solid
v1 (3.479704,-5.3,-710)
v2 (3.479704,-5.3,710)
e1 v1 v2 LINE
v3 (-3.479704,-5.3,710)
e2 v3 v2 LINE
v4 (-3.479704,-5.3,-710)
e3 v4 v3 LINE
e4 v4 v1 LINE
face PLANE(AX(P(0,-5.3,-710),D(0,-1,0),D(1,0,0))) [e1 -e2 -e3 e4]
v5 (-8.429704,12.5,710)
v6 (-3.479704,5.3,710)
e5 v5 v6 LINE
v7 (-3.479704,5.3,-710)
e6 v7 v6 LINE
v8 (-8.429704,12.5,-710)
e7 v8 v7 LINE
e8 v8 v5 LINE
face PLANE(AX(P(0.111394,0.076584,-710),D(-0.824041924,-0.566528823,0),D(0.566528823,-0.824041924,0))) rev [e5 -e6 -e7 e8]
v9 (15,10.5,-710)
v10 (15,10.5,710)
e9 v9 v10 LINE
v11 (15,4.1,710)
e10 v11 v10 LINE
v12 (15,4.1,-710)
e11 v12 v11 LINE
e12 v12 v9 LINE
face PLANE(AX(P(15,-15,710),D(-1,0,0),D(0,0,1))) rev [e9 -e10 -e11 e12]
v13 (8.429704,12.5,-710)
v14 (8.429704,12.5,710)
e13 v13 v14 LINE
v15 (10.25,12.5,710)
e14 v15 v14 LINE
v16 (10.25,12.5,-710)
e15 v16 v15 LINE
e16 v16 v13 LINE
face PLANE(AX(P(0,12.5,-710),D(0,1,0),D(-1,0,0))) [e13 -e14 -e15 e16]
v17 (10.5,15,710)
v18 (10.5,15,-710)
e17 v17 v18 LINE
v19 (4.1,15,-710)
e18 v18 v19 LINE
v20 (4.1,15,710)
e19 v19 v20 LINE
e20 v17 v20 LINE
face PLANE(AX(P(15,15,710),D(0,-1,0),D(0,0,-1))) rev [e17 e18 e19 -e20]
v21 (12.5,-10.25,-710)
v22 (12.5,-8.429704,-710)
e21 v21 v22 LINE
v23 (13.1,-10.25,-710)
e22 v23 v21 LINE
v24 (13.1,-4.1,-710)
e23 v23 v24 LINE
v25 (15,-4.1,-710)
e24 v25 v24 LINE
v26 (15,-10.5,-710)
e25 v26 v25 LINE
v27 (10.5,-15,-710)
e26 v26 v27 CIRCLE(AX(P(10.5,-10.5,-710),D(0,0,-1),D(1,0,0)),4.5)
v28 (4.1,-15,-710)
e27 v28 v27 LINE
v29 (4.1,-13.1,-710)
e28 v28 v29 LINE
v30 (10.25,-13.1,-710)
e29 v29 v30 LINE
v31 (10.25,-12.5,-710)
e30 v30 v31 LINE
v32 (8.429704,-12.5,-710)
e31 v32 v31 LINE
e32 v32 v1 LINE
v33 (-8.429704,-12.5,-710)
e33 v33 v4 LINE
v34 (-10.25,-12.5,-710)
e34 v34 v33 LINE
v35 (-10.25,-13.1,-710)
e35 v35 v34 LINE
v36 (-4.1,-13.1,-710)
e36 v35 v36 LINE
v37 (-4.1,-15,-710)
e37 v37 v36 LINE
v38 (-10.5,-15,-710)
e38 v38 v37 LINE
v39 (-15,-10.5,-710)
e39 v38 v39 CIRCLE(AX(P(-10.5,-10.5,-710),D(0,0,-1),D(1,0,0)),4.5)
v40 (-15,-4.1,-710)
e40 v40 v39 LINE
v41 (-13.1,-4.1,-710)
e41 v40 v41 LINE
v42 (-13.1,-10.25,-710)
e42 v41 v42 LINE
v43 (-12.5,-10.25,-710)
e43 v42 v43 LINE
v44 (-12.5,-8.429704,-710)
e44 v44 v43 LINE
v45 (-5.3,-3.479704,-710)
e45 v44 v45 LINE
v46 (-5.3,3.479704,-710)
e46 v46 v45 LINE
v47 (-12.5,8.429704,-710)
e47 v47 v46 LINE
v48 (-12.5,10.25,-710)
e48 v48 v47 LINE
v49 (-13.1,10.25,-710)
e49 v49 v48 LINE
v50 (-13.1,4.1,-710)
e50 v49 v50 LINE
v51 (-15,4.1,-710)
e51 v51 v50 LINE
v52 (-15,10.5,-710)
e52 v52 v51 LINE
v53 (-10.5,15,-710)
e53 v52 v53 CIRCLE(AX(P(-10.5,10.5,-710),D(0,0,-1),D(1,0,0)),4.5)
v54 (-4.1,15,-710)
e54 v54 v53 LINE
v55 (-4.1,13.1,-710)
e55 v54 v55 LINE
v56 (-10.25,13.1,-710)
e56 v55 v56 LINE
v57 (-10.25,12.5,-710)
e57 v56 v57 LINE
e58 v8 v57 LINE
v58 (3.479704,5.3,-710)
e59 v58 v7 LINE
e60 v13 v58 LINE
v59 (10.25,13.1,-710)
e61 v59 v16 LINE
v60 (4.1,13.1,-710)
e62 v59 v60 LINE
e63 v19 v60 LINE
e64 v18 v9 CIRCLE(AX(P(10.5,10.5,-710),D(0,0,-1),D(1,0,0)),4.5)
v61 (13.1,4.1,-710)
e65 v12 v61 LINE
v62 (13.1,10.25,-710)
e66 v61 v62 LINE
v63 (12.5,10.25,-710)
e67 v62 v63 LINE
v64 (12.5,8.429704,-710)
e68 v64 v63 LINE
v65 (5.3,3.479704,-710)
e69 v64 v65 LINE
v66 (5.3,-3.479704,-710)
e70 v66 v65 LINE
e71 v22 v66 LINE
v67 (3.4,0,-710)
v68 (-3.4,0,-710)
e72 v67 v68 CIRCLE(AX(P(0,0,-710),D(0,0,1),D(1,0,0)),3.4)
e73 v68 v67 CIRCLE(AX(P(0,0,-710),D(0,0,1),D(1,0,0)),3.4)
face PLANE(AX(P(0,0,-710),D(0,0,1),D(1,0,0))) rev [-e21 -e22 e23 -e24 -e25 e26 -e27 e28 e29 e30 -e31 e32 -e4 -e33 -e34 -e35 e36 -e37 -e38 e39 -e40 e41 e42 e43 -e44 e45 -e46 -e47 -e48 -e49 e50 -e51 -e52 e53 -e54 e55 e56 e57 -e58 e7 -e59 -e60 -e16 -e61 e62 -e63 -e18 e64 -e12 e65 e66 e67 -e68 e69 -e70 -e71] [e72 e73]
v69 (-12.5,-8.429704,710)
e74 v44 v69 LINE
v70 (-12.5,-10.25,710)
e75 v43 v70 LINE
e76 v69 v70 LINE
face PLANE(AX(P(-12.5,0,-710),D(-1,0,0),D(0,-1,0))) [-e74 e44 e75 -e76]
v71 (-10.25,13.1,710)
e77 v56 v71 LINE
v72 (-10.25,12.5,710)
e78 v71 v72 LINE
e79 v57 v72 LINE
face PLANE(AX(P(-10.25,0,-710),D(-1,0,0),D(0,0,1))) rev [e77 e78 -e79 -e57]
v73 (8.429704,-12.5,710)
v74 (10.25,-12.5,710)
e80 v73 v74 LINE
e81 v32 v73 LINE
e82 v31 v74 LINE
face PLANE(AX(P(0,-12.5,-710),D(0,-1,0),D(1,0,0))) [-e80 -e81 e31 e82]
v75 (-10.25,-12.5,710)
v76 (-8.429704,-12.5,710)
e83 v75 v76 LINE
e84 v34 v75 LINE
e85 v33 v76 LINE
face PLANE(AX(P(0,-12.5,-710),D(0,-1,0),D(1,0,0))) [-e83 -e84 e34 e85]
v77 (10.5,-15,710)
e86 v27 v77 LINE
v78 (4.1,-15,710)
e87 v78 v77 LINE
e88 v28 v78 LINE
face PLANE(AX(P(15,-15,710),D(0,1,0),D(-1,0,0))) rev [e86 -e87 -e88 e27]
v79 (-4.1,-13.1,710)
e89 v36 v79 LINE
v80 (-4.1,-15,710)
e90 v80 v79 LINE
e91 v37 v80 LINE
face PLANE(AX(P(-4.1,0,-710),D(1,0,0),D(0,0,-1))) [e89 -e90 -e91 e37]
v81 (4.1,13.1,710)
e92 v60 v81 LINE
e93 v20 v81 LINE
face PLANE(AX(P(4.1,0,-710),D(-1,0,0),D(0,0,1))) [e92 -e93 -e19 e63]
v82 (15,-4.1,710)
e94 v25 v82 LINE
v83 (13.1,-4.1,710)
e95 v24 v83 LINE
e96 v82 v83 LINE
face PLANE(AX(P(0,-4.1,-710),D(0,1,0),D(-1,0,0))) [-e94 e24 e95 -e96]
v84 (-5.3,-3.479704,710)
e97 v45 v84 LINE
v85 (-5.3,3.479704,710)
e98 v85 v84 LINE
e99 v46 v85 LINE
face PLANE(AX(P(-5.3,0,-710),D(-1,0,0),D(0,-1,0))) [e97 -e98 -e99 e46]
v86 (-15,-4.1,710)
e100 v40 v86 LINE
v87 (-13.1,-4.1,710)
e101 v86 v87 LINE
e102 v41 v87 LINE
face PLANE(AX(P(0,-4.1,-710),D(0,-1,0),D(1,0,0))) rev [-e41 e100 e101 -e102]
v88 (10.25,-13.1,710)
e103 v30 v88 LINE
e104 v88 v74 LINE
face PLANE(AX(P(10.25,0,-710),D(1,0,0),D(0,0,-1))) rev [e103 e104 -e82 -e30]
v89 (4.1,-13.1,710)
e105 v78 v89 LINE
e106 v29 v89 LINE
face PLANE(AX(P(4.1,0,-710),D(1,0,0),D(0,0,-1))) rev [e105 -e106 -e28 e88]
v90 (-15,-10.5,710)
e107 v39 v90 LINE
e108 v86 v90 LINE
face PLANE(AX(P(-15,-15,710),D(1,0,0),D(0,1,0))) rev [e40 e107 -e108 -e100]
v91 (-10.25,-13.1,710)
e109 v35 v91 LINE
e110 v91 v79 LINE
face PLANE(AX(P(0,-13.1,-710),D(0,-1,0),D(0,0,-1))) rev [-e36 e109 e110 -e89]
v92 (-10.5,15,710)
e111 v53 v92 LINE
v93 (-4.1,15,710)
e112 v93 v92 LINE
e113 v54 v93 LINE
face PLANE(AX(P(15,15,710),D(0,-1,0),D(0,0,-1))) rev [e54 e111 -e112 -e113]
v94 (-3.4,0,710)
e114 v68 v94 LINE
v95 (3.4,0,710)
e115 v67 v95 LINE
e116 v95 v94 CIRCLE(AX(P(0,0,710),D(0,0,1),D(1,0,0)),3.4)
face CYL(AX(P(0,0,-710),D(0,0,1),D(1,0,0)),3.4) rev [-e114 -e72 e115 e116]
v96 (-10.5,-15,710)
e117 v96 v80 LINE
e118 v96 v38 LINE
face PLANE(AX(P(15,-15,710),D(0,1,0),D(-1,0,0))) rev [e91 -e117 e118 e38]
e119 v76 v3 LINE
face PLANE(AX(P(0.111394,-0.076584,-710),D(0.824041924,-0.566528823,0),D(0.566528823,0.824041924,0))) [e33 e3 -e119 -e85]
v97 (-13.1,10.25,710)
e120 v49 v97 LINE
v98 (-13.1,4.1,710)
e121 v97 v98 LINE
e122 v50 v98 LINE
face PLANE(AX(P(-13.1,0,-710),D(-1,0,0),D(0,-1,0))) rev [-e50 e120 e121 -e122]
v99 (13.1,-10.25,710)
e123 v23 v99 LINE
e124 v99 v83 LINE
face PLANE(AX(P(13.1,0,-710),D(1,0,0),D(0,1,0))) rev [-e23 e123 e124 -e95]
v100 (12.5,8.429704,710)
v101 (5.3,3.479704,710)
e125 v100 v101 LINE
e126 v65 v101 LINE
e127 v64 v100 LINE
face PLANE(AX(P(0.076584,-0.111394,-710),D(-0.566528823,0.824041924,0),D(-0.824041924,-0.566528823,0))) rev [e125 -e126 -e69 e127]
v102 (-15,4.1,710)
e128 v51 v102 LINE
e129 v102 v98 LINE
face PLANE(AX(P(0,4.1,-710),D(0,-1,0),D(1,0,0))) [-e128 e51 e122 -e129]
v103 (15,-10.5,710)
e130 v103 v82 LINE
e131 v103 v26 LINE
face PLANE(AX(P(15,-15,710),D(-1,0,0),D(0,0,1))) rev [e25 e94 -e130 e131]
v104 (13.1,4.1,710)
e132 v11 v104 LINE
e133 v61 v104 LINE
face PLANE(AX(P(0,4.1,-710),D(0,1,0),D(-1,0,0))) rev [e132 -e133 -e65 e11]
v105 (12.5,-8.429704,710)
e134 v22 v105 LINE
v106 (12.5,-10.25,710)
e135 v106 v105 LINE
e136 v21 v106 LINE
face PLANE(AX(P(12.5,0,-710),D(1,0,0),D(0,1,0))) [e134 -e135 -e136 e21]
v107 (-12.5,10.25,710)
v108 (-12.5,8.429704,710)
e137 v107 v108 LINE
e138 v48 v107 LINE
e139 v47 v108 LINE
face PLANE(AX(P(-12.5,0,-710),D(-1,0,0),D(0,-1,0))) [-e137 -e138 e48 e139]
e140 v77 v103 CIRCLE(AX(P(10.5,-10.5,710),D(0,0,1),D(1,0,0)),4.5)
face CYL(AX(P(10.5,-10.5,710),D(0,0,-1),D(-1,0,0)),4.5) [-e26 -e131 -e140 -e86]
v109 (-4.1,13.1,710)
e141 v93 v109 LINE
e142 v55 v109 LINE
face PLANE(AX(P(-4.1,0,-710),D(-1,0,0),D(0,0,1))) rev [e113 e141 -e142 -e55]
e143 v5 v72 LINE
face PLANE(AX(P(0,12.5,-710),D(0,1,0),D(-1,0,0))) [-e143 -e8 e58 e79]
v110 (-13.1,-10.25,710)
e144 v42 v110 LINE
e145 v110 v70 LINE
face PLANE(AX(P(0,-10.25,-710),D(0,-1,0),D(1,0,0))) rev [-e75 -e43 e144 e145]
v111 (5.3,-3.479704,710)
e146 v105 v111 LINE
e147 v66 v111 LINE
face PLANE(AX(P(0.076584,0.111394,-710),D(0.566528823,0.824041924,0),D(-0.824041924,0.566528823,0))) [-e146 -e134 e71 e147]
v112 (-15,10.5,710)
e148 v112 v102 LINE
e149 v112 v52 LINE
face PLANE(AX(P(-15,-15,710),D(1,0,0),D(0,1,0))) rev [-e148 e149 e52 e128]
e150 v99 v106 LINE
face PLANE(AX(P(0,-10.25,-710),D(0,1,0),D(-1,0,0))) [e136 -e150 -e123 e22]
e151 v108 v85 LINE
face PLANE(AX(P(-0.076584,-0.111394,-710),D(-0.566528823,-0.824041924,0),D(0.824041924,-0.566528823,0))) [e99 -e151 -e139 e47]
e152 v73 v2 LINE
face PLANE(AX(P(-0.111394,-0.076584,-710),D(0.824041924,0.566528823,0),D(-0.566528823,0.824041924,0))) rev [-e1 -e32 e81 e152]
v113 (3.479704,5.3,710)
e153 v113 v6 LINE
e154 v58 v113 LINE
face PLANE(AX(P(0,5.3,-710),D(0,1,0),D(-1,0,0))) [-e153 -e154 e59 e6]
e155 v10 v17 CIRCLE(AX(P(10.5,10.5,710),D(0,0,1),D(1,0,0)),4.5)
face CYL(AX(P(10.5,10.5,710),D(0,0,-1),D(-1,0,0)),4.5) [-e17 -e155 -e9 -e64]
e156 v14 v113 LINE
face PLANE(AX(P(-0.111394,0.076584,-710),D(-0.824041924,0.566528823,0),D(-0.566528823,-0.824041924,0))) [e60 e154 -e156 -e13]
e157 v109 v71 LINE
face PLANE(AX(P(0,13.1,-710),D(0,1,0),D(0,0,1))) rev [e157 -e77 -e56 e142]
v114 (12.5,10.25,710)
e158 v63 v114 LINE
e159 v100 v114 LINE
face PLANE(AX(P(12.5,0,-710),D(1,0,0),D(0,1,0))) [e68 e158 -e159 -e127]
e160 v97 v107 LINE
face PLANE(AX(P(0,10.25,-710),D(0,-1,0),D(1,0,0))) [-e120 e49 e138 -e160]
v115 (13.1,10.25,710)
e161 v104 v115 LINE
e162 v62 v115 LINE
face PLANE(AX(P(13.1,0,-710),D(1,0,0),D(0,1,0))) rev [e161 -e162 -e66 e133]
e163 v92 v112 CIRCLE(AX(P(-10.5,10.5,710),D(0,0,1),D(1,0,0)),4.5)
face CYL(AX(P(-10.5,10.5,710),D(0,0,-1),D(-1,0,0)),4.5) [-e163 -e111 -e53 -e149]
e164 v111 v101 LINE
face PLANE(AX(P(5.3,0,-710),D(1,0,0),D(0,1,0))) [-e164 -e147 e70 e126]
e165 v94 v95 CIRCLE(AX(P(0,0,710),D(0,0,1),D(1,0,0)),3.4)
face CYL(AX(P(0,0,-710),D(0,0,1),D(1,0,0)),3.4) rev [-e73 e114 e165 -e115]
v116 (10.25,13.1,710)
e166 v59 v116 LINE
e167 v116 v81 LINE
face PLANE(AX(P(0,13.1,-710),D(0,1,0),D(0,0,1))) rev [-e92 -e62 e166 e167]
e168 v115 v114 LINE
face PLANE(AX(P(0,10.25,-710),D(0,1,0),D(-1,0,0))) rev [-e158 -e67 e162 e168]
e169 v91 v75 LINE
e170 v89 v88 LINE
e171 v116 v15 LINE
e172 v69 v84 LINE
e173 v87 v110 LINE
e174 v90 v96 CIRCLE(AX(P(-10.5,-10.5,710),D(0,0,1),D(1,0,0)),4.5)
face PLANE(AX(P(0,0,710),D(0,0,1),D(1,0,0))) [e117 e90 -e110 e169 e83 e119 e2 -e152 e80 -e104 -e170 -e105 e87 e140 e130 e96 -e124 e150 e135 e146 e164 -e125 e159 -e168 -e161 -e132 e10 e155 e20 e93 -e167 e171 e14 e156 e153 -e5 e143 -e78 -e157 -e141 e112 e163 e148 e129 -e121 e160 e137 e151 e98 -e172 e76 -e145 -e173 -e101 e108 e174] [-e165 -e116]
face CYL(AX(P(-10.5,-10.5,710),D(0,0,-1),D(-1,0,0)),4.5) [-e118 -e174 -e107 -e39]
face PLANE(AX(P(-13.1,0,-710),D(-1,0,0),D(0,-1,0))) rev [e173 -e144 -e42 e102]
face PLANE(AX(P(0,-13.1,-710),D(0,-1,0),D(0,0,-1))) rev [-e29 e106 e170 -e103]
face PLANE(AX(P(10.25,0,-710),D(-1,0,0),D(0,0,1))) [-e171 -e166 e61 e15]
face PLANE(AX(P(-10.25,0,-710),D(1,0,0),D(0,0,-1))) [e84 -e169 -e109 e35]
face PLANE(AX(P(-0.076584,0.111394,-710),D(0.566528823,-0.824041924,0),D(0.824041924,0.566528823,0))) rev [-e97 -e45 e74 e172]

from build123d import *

# Parameters (mm, degrees)
SKETCH_1_W               = 30
SKETCH_1_H               = 30
EXTRUDE_1_DEPTH          = 710
FILLET_1_R               = 4.5
SKETCH_2_W               = 8.2
SKETCH_2_H               = 0.3
SKETCH_2_H_2             = 1.9
SKETCH_2_R               = 3.4
CUT_EXTRUDE_1_DEPTH      = 1421.158441865
PATTERN_CIRCULAR_1_COUNT = 4


with BuildPart() as part:
    # 草图1 → 凸台-拉伸1 (new, symmetric)
    with BuildSketch(Plane.XY):
        Rectangle(SKETCH_1_W, SKETCH_1_H)
    extrude(amount=EXTRUDE_1_DEPTH, both=True)

    # 圆角1
    fillet_1_edges = [part.edges().sort_by_distance(p)[0] for p in [
        (-15, 15, 0),
        (15, 15, 0),
        (15, -15, 0),
        (-15, -15, 0),
    ]]
    fillet(fillet_1_edges, radius=FILLET_1_R)

    # 草图2 → 切除-拉伸1 (cut, through all)
    with BuildSketch(Plane.XY.offset(710)):
        with Locations((0, 12.95)):
            Rectangle(SKETCH_2_W, SKETCH_2_H)
        with Locations((0, 14.05)):
            Rectangle(SKETCH_2_W, SKETCH_2_H_2)
        Polygon((10.25, 13.1), (4.1, 13.1), (4.1, 12.8), (-4.1, 12.8), (-4.1, 13.1), (-10.25, 13.1), (-10.25, 12.5), (-8.429704265, 12.5), (8.429704265, 12.5), (10.25, 12.5), align=None)
        Polygon((3.479704265, 5.3), (8.429704265, 12.5), (-8.429704265, 12.5), (-3.479704265, 5.3), align=None)
        Circle(SKETCH_2_R)
    cut_extrude_1 = extrude(amount=-CUT_EXTRUDE_1_DEPTH, mode=Mode.SUBTRACT)

    # 阵列(圆周)1: 切除-拉伸1 ×4 about axis
    pattern_circular_1_axis = Axis((0, 0, 0), (0, 0, 1))
    for i in range(1, PATTERN_CIRCULAR_1_COUNT):
        add(cut_extrude_1.rotate(pattern_circular_1_axis, i * 360 / PATTERN_CIRCULAR_1_COUNT), mode=Mode.SUBTRACT)


solid = part.part
